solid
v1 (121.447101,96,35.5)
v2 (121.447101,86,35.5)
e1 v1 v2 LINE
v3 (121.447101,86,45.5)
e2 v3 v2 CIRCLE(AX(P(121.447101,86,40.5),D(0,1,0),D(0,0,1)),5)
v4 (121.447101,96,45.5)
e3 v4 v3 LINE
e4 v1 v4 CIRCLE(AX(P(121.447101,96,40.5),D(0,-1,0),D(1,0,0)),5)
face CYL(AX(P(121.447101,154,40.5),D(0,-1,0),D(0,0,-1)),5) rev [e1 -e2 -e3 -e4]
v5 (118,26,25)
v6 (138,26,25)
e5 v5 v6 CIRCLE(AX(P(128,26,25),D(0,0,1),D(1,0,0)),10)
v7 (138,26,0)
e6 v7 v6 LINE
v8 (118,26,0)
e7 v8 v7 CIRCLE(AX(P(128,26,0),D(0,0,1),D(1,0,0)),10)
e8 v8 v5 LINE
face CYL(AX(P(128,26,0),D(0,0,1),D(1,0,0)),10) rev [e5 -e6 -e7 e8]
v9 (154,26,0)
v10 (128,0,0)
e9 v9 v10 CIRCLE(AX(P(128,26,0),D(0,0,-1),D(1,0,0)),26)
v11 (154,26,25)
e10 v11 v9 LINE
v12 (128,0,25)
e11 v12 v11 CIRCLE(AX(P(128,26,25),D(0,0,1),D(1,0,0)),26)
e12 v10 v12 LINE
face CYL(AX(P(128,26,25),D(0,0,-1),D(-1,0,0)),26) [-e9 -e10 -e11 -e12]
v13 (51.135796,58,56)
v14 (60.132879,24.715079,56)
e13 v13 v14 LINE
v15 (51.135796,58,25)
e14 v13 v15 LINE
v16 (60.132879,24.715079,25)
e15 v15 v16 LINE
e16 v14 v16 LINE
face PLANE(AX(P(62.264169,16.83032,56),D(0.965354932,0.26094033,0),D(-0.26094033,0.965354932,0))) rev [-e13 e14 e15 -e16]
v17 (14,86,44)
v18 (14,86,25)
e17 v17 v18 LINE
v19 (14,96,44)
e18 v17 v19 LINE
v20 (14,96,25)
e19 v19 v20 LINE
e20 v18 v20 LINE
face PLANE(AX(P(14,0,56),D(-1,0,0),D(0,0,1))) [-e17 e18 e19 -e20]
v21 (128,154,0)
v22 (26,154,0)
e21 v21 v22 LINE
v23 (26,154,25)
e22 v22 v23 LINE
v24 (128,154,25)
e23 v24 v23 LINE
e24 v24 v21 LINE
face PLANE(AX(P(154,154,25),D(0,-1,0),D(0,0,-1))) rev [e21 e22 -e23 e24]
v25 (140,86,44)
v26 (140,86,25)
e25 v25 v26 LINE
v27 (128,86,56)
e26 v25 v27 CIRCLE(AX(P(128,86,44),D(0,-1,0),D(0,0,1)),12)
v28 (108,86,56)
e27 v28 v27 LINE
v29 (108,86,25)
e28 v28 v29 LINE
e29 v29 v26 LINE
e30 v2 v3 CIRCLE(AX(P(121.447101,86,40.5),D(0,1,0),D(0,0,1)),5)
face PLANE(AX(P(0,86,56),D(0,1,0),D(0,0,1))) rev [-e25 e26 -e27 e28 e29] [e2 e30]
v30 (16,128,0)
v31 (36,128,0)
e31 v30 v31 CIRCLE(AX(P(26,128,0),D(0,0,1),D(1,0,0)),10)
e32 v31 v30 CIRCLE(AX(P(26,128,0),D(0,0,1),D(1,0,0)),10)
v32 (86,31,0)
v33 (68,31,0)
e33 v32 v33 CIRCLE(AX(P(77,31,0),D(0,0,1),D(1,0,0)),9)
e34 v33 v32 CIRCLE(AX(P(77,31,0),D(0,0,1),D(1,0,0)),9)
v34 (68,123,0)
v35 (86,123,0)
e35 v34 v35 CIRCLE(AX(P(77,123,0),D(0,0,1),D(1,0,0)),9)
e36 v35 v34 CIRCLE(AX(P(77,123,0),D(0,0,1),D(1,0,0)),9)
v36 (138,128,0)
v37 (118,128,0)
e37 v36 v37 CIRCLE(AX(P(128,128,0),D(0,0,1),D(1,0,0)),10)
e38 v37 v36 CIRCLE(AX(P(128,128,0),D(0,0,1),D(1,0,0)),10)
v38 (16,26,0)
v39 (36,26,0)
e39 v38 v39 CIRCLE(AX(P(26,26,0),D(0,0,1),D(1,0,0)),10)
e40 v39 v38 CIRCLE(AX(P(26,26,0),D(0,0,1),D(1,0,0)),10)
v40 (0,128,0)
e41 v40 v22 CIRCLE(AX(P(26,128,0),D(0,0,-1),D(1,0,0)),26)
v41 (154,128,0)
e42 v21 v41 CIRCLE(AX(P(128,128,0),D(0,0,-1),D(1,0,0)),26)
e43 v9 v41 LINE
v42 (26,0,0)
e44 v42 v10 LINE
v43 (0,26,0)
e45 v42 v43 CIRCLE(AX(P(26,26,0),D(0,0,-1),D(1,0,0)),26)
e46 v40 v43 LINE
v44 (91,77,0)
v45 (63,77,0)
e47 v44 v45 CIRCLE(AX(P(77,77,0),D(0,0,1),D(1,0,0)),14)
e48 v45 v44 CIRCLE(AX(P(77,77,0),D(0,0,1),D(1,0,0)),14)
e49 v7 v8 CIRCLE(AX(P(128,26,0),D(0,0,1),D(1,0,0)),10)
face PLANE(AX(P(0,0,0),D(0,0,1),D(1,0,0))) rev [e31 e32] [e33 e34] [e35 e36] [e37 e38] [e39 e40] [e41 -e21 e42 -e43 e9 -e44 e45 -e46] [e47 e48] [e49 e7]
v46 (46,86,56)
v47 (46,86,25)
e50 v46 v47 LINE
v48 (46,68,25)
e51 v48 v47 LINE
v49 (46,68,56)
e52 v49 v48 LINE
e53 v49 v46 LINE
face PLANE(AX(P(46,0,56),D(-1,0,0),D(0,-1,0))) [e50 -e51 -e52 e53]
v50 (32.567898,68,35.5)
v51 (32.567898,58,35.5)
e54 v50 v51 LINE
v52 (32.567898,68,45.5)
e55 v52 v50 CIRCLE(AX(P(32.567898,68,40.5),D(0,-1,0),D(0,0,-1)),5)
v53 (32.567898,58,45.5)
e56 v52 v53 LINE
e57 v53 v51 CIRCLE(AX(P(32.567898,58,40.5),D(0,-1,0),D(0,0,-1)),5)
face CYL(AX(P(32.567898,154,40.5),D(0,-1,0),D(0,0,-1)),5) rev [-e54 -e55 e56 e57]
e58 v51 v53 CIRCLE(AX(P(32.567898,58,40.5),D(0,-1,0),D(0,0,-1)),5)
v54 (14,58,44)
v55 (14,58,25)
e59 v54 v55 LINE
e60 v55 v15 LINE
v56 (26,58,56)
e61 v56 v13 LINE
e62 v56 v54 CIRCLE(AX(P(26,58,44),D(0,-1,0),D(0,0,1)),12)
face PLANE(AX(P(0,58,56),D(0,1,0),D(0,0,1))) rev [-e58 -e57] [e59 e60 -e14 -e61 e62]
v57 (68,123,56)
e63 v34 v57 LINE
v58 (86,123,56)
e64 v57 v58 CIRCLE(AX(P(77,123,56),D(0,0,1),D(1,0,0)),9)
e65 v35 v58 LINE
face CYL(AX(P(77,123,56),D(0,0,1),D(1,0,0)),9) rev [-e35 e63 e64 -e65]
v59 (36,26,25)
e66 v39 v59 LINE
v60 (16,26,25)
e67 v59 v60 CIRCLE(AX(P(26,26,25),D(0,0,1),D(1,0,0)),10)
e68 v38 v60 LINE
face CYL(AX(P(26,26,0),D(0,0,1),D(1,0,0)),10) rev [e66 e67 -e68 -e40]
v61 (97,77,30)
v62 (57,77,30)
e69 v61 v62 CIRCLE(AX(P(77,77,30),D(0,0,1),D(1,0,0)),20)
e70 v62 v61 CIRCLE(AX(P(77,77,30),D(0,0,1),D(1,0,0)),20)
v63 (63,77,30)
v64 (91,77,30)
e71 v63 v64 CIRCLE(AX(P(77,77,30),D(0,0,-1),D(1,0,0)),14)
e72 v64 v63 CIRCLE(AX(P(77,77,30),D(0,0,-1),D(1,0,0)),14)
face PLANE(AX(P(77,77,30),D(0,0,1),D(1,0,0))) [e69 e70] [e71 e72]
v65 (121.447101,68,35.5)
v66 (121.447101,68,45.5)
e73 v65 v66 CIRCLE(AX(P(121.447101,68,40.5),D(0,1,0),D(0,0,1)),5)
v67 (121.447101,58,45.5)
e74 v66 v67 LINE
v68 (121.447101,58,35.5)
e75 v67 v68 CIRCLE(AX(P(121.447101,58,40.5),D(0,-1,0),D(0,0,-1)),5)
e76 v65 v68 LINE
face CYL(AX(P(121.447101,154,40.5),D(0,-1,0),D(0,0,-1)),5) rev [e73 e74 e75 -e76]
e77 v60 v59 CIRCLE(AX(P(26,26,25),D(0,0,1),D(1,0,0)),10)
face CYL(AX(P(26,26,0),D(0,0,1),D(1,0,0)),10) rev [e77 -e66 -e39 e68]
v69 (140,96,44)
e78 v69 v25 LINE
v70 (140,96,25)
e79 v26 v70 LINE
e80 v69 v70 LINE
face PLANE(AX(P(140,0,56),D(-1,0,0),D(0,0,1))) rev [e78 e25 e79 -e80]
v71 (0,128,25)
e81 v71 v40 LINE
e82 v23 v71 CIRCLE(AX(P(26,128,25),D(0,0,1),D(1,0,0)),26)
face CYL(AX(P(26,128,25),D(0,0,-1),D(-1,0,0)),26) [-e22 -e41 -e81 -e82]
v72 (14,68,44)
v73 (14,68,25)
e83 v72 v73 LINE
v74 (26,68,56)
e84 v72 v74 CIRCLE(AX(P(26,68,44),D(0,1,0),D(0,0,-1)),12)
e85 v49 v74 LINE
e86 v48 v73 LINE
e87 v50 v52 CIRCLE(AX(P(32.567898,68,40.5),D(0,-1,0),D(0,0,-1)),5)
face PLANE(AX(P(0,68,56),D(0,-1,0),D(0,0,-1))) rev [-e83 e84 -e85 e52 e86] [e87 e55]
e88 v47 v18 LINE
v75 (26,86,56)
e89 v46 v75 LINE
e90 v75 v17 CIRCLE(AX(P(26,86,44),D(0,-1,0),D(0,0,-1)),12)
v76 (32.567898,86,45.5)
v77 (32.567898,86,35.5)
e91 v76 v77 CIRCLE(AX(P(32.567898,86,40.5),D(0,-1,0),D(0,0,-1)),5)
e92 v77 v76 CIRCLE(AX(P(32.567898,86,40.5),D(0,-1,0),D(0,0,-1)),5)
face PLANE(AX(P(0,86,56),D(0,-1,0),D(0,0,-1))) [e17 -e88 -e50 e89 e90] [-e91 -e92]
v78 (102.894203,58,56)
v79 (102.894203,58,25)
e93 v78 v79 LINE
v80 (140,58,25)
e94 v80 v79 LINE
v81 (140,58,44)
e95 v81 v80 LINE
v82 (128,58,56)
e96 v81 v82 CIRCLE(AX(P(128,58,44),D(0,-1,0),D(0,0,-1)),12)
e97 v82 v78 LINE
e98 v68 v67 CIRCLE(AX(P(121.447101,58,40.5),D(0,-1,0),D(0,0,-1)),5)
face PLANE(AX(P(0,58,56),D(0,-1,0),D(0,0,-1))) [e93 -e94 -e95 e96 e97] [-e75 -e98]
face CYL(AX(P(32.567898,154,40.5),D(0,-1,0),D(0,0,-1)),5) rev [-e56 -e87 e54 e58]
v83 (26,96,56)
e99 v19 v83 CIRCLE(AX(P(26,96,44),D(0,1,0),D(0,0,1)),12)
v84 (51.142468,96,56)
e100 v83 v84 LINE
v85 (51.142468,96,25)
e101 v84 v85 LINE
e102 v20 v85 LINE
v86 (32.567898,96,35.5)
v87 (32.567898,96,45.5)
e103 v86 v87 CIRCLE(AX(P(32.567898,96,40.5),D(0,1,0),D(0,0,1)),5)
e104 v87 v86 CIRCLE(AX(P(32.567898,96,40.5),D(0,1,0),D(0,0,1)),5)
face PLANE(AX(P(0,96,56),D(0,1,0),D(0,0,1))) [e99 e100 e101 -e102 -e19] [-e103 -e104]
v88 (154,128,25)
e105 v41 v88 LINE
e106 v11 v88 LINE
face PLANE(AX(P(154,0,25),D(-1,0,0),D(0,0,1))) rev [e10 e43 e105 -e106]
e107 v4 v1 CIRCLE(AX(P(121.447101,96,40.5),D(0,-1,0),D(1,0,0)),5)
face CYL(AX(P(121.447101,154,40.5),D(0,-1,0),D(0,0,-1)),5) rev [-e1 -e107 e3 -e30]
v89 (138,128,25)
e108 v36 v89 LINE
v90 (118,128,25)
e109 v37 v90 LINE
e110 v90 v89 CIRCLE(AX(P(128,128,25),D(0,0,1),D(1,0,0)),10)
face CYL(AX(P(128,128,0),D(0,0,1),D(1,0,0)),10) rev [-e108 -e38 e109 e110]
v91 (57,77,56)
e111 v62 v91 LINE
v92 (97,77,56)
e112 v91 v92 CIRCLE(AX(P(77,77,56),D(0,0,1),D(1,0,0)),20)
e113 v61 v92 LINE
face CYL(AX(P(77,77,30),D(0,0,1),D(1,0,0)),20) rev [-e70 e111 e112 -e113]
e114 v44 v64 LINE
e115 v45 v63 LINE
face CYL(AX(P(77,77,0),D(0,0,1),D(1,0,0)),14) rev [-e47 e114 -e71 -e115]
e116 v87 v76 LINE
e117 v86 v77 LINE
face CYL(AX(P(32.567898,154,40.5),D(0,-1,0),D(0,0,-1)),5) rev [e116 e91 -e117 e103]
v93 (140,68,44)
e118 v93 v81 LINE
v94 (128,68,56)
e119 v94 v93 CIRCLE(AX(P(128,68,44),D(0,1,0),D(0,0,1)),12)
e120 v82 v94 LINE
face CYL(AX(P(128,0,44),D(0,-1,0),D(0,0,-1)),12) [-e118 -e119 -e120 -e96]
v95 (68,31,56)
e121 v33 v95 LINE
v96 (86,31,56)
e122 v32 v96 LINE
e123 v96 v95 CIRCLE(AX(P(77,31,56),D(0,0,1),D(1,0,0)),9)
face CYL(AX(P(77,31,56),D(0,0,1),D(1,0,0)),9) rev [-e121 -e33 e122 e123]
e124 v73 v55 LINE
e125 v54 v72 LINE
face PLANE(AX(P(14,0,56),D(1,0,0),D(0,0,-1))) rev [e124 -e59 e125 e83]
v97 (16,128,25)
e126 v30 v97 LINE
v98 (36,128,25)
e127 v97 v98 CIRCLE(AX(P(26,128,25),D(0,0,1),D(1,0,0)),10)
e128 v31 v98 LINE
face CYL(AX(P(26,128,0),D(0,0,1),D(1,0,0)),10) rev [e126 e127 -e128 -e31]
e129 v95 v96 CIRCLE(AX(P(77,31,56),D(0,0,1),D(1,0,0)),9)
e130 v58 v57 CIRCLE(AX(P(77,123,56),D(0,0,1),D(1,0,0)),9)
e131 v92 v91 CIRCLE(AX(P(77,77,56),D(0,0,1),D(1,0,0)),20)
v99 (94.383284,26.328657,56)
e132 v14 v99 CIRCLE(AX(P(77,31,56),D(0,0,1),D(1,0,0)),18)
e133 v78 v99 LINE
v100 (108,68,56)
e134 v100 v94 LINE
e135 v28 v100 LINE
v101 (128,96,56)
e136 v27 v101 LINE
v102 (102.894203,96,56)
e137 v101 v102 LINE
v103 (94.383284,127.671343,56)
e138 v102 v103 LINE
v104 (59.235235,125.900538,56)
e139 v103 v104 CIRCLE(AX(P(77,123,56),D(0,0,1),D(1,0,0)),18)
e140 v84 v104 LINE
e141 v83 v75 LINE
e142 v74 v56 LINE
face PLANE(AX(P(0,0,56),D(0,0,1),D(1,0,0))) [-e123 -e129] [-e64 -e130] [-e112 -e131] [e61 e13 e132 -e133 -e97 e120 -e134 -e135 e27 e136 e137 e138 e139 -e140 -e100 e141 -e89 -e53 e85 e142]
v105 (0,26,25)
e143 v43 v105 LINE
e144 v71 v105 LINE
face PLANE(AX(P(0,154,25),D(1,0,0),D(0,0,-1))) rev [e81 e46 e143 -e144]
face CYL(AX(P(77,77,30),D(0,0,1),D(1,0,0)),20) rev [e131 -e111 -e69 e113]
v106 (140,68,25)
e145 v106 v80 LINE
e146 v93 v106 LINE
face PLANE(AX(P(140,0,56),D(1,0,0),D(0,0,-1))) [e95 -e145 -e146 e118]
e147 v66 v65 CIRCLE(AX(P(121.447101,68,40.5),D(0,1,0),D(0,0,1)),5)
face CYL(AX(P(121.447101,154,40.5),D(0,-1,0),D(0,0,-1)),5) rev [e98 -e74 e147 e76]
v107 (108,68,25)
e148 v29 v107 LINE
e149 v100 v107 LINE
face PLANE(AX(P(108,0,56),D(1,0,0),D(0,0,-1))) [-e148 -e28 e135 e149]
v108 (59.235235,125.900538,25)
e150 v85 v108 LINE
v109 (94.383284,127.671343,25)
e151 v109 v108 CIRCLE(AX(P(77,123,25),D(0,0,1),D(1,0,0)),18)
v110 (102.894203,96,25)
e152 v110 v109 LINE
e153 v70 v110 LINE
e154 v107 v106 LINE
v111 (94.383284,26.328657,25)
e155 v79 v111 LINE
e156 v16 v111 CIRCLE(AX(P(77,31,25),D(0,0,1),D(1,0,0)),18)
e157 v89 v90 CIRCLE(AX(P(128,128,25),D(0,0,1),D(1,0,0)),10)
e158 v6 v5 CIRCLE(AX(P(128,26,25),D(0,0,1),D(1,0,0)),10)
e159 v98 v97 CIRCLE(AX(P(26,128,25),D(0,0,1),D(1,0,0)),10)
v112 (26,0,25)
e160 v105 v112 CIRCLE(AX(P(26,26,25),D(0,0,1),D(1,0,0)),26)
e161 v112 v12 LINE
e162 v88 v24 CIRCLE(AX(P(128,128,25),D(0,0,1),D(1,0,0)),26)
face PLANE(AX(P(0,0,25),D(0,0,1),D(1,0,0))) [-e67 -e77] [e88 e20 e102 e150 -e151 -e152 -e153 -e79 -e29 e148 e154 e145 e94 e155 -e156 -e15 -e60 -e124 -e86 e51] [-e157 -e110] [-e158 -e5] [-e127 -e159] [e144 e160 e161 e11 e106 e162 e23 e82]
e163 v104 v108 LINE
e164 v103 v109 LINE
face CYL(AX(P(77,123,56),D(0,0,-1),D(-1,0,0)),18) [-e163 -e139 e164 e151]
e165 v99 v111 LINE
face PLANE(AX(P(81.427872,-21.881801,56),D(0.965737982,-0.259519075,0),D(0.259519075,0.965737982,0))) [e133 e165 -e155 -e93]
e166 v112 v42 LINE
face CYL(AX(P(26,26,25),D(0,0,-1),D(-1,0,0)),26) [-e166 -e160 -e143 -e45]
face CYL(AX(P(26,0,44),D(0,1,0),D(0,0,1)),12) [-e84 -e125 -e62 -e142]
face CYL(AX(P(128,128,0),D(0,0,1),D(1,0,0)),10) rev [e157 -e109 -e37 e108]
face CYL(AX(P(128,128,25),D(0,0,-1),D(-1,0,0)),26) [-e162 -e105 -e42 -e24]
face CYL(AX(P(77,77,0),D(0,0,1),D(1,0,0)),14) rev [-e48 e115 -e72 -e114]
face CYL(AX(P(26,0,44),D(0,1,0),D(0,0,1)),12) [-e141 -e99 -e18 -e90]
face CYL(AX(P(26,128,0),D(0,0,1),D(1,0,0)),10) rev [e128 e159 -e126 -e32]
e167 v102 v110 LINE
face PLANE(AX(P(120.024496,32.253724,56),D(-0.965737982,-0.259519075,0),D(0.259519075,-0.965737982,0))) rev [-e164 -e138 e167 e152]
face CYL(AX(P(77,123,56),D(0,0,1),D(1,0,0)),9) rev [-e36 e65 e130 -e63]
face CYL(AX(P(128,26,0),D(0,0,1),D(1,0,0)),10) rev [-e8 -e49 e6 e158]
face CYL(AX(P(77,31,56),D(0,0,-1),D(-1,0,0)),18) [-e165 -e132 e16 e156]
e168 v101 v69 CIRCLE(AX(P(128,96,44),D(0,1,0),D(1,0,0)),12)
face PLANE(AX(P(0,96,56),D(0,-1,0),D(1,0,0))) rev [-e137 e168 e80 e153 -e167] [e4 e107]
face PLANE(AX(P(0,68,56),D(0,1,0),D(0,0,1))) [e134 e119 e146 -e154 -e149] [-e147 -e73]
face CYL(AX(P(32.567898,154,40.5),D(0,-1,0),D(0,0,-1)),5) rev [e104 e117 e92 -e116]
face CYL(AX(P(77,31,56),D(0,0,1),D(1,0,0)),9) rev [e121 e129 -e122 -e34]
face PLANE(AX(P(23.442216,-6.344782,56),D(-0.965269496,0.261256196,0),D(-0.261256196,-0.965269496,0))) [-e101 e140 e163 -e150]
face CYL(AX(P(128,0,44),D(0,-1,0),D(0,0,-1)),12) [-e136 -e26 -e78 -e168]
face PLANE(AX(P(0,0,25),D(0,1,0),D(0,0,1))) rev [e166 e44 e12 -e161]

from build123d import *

# Parameters (mm, degrees)
BASE_PLATE_SKETCH_W        = 154
BASE_PLATE_SKETCH_H        = 154
BASE_PLATE_DEPTH           = 25
PLATE_CORNER_FILLETS_R26_R = 26
CORNER_HOLES_SKETCH_R      = 10
CORNER_HOLES_4X_20_DEPTH   = 25
CENTRAL_HUB_BOSS_DEPTH     = 31
CENTRE_TAP_DRILL_M20X2_0_D = 18
COUNTERBORE_SKETCH_R       = 14
COUNTERBORE_28_DEPTH       = 225.873297659
BORE_STEP_SKETCH_R         = 20
BORE_STEP_CUT_DEPTH        = 26
LUG_SLOT_A_SKETCH_R        = 5
LUG_SLOT_A_DEPTH           = 190.915770804
LUG_SLOT_B_SKETCH_R        = 5
LUG_SLOT_B_DEPTH           = 190.915770804
HUB_FILLETS_R12_R          = 12


with BuildPart() as part:
    # Base Plate Sketch → Base Plate (new body)
    with BuildSketch(Plane.XY):
        with Locations((77, 77)):
            Rectangle(BASE_PLATE_SKETCH_W, BASE_PLATE_SKETCH_H)
    extrude(amount=BASE_PLATE_DEPTH)

    # Plate Corner Fillets R26
    plate_corner_fillets_r26_edges = [part.edges().sort_by_distance(p)[0] for p in [
        (0, 154, 12.5),
        (154, 154, 12.5),
        (154, 0, 12.5),
        (0, 0, 12.5),
    ]]
    fillet(plate_corner_fillets_r26_edges, radius=PLATE_CORNER_FILLETS_R26_R)

    # Corner Holes Sketch → Corner Holes 4xØ20 (cut)
    with BuildSketch(Plane.XY.offset(25)):
        with Locations((26, 128)):
            Circle(CORNER_HOLES_SKETCH_R)
        with Locations((128, 128)):
            Circle(CORNER_HOLES_SKETCH_R)
        with Locations((128, 26)):
            Circle(CORNER_HOLES_SKETCH_R)
        with Locations((26, 26)):
            Circle(CORNER_HOLES_SKETCH_R)
    extrude(amount=-CORNER_HOLES_4X_20_DEPTH, mode=Mode.SUBTRACT)

    # Hub Profile Sketch → Central Hub Boss (add)
    with BuildSketch(Plane.XY.offset(25)):
        with BuildLine():
            Line((14, 58), (51.135796279, 58))
            Line((51.135796279, 58), (59.2634951, 27.931385667))
            Line((59.2634951, 27.931385667), (60.132879108, 24.715078934))
            ThreePointArc((60.132879108, 24.715078934), (77.84706214, 13.019941999), (94.383283675, 26.328656654))
            Line((94.383283675, 26.328656654), (102.894202658, 58))
            Line((102.894202658, 58), (140, 58))
            Line((140, 58), (140, 68))
            Line((140, 68), (108, 68))
            Line((108, 68), (108, 77))
            Line((108, 77), (108, 86))
            Line((108, 86), (140, 86))
            Line((140, 86), (140, 96))
            Line((140, 96), (102.894202658, 96))
            Line((102.894202658, 96), (94.383283675, 127.671343346))
            ThreePointArc((94.383283675, 127.671343346), (76.094284636, 140.977198883), (59.23523482, 125.900537557))
            Line((59.23523482, 125.900537557), (51.142468246, 96))
            Line((51.142468246, 96), (14, 96))
            Line((14, 96), (14, 86))
            Line((14, 86), (46, 86))
            Line((46, 86), (46, 77))
            Line((46, 77), (46, 68))
            Line((46, 68), (14, 68))
            Line((14, 68), (14, 58))
        make_face()
    extrude(amount=CENTRAL_HUB_BOSS_DEPTH)

    # Centre Tap Drill M20x2.0 (through all)
    with Locations(Plane.XY.offset(56)):
        with Locations((77, 123), (77, 31)):
            Hole(CENTRE_TAP_DRILL_M20X2_0_D / 2)

    # Counterbore Sketch → Counterbore Ø28 (cut, through all)
    with BuildSketch(Plane.XY.offset(56)):
        with Locations((77, 77)):
            Circle(COUNTERBORE_SKETCH_R)
    extrude(amount=-COUNTERBORE_28_DEPTH, mode=Mode.SUBTRACT)

    # Bore Step Sketch → Bore Step Cut (cut)
    with BuildSketch(Plane.XY.offset(56)):
        with Locations((77, 77)):
            Circle(BORE_STEP_SKETCH_R)
    extrude(amount=-BORE_STEP_CUT_DEPTH, mode=Mode.SUBTRACT)

    # Lug Slot A Sketch → Lug Slot A (cut, through all)
    with BuildSketch(Plane.XZ.offset(-58)):
        with Locations(Location((32.567898139, 40.5, 0), (0, 0, 270))):
            Circle(LUG_SLOT_A_SKETCH_R)
    extrude(amount=-LUG_SLOT_A_DEPTH, mode=Mode.SUBTRACT)

    # Lug Slot B Sketch → Lug Slot B (cut, through all)
    with BuildSketch(Plane.XZ.offset(-58)):
        with Locations((121.447101329, 40.5)):
            Circle(LUG_SLOT_B_SKETCH_R)
    extrude(amount=-LUG_SLOT_B_DEPTH, mode=Mode.SUBTRACT)

    # Hub Fillets R12
    hub_fillets_r12_edges = [part.edges().sort_by_distance(p)[0] for p in [
        (140, 63, 56),
        (14, 91, 56),
        (140, 91, 56),
        (14, 63, 56),
    ]]
    fillet(hub_fillets_r12_edges, radius=HUB_FILLETS_R12_R)


solid = part.part
